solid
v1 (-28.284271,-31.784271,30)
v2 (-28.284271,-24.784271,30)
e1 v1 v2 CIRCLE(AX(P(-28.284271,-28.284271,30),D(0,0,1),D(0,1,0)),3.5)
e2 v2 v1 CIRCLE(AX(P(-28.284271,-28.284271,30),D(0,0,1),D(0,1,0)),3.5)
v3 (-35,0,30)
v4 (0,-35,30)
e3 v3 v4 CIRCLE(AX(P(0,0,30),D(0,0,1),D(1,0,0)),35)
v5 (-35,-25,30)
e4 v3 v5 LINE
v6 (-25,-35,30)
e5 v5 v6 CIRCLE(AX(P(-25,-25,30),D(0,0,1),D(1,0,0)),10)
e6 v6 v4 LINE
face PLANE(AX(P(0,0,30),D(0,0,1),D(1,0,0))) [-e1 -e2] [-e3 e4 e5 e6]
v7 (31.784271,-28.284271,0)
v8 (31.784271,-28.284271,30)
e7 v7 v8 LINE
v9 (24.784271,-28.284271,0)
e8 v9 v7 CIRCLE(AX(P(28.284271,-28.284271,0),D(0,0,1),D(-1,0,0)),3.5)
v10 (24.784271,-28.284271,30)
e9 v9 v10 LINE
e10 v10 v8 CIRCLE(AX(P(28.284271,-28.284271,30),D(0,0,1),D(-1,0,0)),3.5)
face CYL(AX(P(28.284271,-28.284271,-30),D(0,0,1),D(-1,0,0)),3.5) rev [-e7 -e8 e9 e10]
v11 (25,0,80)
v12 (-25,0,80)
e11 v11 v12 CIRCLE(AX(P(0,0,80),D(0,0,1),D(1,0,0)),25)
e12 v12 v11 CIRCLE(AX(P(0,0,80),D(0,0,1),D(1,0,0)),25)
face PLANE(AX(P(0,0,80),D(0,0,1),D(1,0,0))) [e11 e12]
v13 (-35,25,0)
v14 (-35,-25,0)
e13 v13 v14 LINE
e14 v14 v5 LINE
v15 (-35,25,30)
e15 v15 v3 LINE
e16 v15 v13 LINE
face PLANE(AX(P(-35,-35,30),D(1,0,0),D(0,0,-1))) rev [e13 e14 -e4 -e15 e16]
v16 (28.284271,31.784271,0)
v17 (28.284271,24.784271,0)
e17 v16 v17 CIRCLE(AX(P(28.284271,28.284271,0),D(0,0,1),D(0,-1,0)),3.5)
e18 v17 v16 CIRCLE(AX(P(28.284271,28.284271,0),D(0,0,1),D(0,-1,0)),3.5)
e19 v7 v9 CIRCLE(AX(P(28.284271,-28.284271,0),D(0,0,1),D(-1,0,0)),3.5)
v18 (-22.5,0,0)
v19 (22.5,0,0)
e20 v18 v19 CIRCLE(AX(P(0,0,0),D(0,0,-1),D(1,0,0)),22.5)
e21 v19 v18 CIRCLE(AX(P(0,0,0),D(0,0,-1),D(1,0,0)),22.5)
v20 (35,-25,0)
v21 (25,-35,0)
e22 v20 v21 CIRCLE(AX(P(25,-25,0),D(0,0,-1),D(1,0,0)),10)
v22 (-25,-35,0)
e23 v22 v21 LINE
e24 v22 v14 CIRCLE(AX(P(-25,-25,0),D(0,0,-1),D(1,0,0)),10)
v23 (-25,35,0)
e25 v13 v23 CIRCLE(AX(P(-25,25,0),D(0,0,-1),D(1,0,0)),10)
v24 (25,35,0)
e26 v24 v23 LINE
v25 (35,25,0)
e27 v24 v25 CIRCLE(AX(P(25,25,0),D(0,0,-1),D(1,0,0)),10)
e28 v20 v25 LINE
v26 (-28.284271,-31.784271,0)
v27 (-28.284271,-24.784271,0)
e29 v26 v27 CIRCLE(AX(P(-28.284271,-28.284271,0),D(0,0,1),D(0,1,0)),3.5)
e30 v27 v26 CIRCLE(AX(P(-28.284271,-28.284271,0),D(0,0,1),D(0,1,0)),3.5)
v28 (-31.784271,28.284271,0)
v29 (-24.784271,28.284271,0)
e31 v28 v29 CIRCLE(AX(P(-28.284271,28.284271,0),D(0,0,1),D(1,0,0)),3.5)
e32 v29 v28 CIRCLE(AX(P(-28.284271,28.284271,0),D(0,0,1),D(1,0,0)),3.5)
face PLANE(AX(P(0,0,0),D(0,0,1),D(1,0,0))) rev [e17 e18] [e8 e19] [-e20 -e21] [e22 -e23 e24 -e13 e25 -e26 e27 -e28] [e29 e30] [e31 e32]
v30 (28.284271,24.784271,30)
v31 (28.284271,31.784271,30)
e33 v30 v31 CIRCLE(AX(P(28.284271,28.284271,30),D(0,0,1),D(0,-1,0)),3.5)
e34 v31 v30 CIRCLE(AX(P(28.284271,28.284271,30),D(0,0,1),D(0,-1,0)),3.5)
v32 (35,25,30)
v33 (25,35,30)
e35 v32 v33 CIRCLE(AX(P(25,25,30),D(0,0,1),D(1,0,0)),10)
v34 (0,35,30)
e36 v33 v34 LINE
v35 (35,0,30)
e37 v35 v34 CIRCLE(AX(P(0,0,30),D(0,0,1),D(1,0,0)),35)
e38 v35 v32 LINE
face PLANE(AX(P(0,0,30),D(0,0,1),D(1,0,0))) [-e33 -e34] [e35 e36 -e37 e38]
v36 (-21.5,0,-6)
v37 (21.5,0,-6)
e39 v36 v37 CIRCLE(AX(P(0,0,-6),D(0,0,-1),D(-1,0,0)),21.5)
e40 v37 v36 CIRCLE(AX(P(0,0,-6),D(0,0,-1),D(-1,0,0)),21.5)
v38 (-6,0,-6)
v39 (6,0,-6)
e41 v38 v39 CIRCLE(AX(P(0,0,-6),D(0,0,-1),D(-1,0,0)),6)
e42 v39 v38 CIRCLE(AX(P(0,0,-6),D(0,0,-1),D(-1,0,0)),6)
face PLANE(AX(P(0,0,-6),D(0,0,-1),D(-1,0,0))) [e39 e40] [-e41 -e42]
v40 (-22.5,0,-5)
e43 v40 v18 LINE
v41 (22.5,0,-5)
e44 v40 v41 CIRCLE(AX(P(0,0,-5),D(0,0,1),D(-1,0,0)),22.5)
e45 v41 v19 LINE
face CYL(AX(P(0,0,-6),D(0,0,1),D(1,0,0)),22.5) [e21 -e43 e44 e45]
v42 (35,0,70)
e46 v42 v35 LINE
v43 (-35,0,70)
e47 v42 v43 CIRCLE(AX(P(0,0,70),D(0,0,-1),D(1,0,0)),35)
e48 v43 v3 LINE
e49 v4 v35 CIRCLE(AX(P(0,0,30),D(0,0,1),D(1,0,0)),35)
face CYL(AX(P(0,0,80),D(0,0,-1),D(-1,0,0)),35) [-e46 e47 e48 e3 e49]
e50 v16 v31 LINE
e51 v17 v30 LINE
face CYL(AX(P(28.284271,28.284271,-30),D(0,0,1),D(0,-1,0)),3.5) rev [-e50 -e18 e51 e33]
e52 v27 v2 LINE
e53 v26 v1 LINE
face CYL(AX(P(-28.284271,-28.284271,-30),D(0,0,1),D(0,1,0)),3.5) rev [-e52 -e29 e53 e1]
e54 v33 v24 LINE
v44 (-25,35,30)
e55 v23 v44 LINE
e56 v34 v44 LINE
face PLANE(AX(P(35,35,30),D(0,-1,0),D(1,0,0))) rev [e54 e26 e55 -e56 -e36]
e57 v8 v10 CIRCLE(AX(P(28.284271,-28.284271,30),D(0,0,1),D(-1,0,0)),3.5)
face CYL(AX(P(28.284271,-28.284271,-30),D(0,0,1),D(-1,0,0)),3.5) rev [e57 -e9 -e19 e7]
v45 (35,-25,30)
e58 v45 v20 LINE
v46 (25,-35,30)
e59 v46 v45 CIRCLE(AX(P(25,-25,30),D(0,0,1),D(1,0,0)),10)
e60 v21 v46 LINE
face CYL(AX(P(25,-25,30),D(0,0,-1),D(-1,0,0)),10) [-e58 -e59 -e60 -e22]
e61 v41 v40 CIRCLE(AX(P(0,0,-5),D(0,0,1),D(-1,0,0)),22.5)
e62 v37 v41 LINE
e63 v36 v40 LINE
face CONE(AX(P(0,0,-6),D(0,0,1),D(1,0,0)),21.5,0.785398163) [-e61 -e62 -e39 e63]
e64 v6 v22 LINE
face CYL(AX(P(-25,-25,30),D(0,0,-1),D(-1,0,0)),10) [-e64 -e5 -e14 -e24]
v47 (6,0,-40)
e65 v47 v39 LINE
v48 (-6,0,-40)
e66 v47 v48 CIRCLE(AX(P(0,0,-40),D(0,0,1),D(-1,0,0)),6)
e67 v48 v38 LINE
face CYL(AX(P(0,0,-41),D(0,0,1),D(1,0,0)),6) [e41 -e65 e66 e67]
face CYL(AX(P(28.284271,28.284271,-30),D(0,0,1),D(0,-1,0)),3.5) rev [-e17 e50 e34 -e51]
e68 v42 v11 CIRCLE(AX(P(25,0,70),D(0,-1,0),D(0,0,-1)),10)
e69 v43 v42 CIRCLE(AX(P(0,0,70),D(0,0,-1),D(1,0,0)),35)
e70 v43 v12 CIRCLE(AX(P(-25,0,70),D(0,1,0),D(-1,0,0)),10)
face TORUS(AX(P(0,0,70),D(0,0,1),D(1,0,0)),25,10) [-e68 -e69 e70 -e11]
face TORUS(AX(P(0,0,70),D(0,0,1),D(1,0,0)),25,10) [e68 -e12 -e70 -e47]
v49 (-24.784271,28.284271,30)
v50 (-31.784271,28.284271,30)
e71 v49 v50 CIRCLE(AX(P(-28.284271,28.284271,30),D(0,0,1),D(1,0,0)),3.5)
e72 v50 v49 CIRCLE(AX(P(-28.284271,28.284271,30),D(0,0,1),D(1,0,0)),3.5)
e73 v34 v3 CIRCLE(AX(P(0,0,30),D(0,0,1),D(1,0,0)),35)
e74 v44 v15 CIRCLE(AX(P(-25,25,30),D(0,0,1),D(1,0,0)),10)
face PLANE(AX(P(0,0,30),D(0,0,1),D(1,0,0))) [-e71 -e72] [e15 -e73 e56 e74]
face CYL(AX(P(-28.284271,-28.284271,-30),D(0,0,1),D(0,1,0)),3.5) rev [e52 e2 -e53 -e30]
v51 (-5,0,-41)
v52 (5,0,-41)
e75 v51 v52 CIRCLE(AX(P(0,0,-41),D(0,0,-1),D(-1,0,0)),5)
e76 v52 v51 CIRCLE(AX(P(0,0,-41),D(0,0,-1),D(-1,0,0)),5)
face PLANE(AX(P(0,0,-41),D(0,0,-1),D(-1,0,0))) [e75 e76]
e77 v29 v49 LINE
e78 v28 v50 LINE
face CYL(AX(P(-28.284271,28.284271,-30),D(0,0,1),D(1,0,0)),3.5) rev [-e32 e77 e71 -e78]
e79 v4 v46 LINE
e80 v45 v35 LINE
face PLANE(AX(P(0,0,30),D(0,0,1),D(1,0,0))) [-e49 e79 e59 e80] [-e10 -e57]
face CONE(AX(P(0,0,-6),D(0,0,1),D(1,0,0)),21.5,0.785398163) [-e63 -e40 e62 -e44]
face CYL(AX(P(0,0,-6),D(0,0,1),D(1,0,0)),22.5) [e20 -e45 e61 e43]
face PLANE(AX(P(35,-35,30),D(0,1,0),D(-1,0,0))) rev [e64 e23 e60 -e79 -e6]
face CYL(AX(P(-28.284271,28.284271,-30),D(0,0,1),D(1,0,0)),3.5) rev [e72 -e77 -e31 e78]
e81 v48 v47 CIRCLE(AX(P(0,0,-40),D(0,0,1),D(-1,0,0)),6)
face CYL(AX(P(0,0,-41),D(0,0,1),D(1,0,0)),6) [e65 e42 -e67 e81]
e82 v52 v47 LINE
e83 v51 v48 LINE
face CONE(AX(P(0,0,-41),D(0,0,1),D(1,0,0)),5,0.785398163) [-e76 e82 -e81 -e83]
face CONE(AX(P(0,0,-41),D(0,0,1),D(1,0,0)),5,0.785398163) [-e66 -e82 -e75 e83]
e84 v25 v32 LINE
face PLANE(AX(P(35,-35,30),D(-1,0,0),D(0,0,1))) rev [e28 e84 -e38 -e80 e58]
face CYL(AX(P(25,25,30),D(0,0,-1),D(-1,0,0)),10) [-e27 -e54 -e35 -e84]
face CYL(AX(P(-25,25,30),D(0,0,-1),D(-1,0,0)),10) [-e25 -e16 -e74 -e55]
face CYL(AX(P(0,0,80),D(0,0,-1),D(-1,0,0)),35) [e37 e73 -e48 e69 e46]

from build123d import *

# Parameters (mm, degrees)
SKETCH1_W           = 70
SKETCH1_H           = 70
BOSS_EXTRUDE1_DEPTH = 30
FILLET2_R           = 10
SKETCH3_R           = 3.5
CUT_EXTRUDE1_DEPTH  = 60
SKETCH4_R           = 22.5
BOSS_EXTRUDE3_DEPTH = 6
SKETCH5_R           = 6
BOSS_EXTRUDE4_DEPTH = 35
CHAMFER1_SIZE       = 1
CHAMFER2_SIZE       = 1
CIRPATTERN1_COUNT   = 4
SKETCH6_R           = 35
BOSS_EXTRUDE5_DEPTH = 50
FILLET3_R           = 10


with BuildPart() as part:
    # Sketch1 → Boss-Extrude1 (new body)
    with BuildSketch(Plane.XY):
        Rectangle(SKETCH1_W, SKETCH1_H)
    extrude(amount=BOSS_EXTRUDE1_DEPTH)

    # Fillet2
    fillet2_edges = [part.edges().sort_by_distance(p)[0] for p in [
        (-35, 35, 15),
        (35, 35, 15),
        (35, -35, 15),
        (-35, -35, 15),
    ]]
    fillet(fillet2_edges, radius=FILLET2_R)

    # Sketch3 → Cut-Extrude1 (cut)
    with BuildSketch(Plane.XY.offset(30)):
        with Locations((-28.284271247, 28.284271247)):
            Circle(SKETCH3_R)
    cut_extrude1 = extrude(amount=-CUT_EXTRUDE1_DEPTH, mode=Mode.SUBTRACT)

    # Sketch4 → Boss-Extrude3 (add)
    with BuildSketch(Plane(origin=(0, 0, 0), x_dir=(-1, 0, 0), z_dir=(0, 0, -1))):
        with Locations(Location((0, 0, 0), (0, 0, 180))):
            Circle(SKETCH4_R)
    extrude(amount=BOSS_EXTRUDE3_DEPTH)

    # Sketch5 → Boss-Extrude4 (add)
    with BuildSketch(Plane(origin=(0, 0, -6), x_dir=(-1, 0, 0), z_dir=(0, 0, -1))):
        Circle(SKETCH5_R)
    extrude(amount=BOSS_EXTRUDE4_DEPTH)

    # Chamfer1
    chamfer1_edges = [part.edges().sort_by_distance(p)[0] for p in [
        (6, 0, -41),
    ]]
    chamfer(chamfer1_edges, length=CHAMFER1_SIZE)

    # Chamfer2
    chamfer2_edges = [part.edges().sort_by_distance(p)[0] for p in [
        (-22.5, 0, -6),
    ]]
    chamfer(chamfer2_edges, length=CHAMFER2_SIZE)

    # CirPattern1: Cut-Extrude1 ×4 about axis
    cirpattern1_axis = Axis((0, 0, 0), (0, 0, 1))
    for i in range(1, CIRPATTERN1_COUNT):
        add(cut_extrude1.rotate(cirpattern1_axis, i * 360 / CIRPATTERN1_COUNT), mode=Mode.SUBTRACT)

    # Sketch6 → Boss-Extrude5 (add)
    with BuildSketch(Plane.XY.offset(30)):
        Circle(SKETCH6_R)
    extrude(amount=BOSS_EXTRUDE5_DEPTH)

    # Fillet3
    fillet3_edges = [part.edges().sort_by_distance(p)[0] for p in [
        (-35, 0, 80),
    ]]
    fillet(fillet3_edges, radius=FILLET3_R)


solid = part.part
